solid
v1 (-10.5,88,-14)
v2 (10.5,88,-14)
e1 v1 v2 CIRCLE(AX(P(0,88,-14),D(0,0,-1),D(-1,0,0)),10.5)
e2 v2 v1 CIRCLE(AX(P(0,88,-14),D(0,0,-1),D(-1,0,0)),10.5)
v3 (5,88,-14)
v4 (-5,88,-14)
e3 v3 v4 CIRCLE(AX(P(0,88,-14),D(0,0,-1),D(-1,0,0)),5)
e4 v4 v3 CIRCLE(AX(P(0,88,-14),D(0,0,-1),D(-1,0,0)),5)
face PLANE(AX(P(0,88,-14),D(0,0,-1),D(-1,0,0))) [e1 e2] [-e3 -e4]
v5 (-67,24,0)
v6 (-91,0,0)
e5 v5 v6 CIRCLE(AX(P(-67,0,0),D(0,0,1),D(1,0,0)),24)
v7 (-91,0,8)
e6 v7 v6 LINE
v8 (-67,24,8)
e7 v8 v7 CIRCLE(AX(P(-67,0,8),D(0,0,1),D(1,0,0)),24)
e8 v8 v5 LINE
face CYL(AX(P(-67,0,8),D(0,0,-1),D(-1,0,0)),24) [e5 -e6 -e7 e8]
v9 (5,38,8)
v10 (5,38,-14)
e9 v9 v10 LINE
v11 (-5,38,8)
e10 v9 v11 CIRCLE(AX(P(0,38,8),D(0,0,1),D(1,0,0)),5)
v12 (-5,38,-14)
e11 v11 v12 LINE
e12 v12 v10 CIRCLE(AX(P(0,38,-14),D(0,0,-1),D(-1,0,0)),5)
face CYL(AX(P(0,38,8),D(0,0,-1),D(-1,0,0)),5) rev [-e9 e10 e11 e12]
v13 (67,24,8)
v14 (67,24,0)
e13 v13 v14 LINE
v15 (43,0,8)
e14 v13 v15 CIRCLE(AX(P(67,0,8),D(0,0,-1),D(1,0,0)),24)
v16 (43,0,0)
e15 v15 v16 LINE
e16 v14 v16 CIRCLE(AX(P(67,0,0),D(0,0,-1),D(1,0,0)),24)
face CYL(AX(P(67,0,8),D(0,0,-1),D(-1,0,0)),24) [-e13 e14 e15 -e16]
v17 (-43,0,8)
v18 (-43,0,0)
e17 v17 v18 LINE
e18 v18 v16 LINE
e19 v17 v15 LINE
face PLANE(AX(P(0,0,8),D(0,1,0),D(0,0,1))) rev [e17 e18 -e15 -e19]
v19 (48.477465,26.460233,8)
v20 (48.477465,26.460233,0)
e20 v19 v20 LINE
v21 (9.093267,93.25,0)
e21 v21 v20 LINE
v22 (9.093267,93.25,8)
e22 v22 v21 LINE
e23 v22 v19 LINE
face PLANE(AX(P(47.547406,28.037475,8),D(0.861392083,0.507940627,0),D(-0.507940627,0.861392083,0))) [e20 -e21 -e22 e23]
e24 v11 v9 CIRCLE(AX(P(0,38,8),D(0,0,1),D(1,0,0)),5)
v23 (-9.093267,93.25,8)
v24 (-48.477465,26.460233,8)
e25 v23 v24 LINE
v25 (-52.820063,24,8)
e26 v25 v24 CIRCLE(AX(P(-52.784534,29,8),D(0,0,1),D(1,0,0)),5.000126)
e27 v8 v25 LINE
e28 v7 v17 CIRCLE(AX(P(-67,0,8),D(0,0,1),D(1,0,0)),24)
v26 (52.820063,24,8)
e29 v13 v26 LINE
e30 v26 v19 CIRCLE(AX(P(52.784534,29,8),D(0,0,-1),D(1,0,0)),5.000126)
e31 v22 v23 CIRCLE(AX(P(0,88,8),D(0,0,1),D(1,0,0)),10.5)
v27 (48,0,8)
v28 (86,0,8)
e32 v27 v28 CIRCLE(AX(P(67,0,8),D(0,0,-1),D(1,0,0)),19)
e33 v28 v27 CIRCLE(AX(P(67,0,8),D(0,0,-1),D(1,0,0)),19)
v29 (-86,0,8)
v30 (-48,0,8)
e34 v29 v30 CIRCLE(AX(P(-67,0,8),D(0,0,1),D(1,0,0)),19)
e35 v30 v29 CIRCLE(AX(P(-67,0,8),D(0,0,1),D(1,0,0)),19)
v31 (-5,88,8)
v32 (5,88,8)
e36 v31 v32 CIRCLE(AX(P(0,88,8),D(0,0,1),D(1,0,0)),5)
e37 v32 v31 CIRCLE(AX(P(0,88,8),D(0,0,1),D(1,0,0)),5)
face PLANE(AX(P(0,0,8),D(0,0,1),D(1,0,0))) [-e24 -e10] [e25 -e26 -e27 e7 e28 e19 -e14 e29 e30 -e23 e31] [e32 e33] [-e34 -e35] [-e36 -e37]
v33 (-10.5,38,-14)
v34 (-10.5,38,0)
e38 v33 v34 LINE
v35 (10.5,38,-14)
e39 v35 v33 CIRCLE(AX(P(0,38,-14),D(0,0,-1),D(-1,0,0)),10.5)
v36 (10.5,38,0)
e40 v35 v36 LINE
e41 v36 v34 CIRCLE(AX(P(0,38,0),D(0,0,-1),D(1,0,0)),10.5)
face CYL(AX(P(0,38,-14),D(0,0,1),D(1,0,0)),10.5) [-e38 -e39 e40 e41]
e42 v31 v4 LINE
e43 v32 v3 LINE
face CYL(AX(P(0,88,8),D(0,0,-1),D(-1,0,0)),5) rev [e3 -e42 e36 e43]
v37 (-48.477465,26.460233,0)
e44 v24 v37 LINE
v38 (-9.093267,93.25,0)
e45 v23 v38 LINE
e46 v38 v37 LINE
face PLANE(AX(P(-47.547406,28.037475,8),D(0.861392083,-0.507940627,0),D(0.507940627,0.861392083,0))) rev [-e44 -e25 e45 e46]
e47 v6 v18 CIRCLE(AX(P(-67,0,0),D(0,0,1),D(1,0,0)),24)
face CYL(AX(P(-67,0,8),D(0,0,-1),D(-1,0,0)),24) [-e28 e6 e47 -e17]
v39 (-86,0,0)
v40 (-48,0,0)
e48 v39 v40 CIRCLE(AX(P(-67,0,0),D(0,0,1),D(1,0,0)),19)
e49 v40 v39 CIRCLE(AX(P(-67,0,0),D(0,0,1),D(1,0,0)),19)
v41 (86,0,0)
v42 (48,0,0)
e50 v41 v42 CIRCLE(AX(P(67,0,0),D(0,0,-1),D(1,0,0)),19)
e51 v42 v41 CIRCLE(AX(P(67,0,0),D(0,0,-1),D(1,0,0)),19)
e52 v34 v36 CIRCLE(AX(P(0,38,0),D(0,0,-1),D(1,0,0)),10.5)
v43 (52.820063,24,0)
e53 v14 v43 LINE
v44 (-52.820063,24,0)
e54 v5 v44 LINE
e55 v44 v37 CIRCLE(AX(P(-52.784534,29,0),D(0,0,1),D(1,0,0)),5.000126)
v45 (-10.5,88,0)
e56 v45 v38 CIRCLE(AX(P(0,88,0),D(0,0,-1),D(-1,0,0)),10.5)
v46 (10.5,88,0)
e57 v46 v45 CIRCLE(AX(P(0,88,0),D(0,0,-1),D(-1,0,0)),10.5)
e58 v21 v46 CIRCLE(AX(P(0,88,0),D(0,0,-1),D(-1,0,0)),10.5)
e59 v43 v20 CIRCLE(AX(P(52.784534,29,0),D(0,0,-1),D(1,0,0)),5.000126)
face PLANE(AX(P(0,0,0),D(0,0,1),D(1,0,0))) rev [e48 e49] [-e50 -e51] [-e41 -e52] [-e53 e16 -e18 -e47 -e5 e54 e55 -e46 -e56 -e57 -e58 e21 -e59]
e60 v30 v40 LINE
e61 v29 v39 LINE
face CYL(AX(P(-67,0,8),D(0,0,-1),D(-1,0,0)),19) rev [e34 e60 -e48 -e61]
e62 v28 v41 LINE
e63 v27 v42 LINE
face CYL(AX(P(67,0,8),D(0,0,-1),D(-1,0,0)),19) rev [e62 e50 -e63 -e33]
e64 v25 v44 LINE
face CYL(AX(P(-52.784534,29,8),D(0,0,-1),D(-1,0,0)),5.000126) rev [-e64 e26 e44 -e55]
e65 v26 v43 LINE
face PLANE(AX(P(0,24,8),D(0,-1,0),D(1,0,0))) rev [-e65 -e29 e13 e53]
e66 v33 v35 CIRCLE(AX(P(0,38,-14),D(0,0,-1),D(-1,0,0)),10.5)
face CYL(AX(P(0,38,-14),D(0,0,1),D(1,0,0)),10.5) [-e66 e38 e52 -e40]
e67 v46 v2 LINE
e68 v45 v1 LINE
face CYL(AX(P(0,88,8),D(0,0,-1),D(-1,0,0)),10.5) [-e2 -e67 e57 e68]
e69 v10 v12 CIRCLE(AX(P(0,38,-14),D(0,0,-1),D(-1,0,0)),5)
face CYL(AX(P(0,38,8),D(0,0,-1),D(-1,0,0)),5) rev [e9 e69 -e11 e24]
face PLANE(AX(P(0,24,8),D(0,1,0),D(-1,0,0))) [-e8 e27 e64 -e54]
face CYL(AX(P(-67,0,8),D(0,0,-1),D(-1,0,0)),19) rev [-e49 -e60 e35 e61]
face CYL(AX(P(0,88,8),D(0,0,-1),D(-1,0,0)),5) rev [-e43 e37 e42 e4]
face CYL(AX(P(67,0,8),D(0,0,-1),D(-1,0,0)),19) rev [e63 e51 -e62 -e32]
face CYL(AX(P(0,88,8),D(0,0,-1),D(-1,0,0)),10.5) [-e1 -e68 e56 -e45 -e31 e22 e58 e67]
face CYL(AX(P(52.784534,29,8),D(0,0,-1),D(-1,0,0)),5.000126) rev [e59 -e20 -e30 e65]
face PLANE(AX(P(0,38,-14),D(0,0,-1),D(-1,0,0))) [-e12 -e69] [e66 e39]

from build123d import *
from build123d.topology import SkipClean

# Parameters (mm, degrees)
SKETCH_1_R      = 19
SKETCH_1_R_2    = 5
EXTRUDE_1_DEPTH = 8
EXTRUDE_START   = 14
SKETCH_3_R      = 10.5
SKETCH_3_R_2    = 5
EXTRUDE_3_DEPTH = 14


with BuildPart() as part:
    # 草图1 → 凸台-拉伸1 (new body)
    with BuildSketch(Plane.XY):
        with BuildLine():
            ThreePointArc((-67, 24), (-83.970562748, -16.970562748), (-43, 0))
            Line((-43, 0), (43, 0))
            ThreePointArc((43, 0), (83.970562748, -16.970562748), (67, 24))
            Line((67, 24), (52.820062564, 24))
            ThreePointArc((52.820062564, 24), (50.319842999, 24.649533151), (48.477464605, 26.460232751))
            Line((48.477464605, 26.460232751), (9.09326674, 93.25))
            ThreePointArc((9.09326674, 93.25), (0, 98.5), (-9.09326674, 93.25))
            Line((-9.09326674, 93.25), (-48.477464605, 26.460232751))
            ThreePointArc((-48.477464605, 26.460232751), (-50.319842999, 24.649533151), (-52.820062564, 24))
            Line((-52.820062564, 24), (-67, 24))
        make_face()
        with Locations((-67, 0)):
            Circle(SKETCH_1_R, mode=Mode.SUBTRACT)
        with Locations((67, 0)):
            Circle(SKETCH_1_R, mode=Mode.SUBTRACT)
        with Locations((0, 38)):
            Circle(SKETCH_1_R_2, mode=Mode.SUBTRACT)
        with Locations((0, 88)):
            Circle(SKETCH_1_R_2, mode=Mode.SUBTRACT)
    extrude(amount=EXTRUDE_1_DEPTH)

    # 草图3 → 凸台-拉伸3 (add)
    # profile 1 of 2: a face of its own
    with SkipClean():  # the faces are left unmerged after this step: merging them gives an invalid solid
        with BuildSketch(Plane(origin=(0, 0, 0), x_dir=(-1, 0, 0), z_dir=(0, 0, -1)).offset(EXTRUDE_START)):
            with Locations((0, 88)):
                Circle(SKETCH_3_R)
            with Locations((0, 88)):
                Circle(SKETCH_3_R_2, mode=Mode.SUBTRACT)
        # profile 2 of 2: a face of its own
        with BuildSketch(Plane(origin=(0, 0, 0), x_dir=(-1, 0, 0), z_dir=(0, 0, -1)).offset(EXTRUDE_START)):
            with Locations(Location((0, 38, 0), (0, 0, 180))):
                Circle(SKETCH_3_R)
            with Locations((0, 38)):
                Circle(SKETCH_3_R_2, mode=Mode.SUBTRACT)
        extrude(amount=-EXTRUDE_3_DEPTH)


solid = part.part
